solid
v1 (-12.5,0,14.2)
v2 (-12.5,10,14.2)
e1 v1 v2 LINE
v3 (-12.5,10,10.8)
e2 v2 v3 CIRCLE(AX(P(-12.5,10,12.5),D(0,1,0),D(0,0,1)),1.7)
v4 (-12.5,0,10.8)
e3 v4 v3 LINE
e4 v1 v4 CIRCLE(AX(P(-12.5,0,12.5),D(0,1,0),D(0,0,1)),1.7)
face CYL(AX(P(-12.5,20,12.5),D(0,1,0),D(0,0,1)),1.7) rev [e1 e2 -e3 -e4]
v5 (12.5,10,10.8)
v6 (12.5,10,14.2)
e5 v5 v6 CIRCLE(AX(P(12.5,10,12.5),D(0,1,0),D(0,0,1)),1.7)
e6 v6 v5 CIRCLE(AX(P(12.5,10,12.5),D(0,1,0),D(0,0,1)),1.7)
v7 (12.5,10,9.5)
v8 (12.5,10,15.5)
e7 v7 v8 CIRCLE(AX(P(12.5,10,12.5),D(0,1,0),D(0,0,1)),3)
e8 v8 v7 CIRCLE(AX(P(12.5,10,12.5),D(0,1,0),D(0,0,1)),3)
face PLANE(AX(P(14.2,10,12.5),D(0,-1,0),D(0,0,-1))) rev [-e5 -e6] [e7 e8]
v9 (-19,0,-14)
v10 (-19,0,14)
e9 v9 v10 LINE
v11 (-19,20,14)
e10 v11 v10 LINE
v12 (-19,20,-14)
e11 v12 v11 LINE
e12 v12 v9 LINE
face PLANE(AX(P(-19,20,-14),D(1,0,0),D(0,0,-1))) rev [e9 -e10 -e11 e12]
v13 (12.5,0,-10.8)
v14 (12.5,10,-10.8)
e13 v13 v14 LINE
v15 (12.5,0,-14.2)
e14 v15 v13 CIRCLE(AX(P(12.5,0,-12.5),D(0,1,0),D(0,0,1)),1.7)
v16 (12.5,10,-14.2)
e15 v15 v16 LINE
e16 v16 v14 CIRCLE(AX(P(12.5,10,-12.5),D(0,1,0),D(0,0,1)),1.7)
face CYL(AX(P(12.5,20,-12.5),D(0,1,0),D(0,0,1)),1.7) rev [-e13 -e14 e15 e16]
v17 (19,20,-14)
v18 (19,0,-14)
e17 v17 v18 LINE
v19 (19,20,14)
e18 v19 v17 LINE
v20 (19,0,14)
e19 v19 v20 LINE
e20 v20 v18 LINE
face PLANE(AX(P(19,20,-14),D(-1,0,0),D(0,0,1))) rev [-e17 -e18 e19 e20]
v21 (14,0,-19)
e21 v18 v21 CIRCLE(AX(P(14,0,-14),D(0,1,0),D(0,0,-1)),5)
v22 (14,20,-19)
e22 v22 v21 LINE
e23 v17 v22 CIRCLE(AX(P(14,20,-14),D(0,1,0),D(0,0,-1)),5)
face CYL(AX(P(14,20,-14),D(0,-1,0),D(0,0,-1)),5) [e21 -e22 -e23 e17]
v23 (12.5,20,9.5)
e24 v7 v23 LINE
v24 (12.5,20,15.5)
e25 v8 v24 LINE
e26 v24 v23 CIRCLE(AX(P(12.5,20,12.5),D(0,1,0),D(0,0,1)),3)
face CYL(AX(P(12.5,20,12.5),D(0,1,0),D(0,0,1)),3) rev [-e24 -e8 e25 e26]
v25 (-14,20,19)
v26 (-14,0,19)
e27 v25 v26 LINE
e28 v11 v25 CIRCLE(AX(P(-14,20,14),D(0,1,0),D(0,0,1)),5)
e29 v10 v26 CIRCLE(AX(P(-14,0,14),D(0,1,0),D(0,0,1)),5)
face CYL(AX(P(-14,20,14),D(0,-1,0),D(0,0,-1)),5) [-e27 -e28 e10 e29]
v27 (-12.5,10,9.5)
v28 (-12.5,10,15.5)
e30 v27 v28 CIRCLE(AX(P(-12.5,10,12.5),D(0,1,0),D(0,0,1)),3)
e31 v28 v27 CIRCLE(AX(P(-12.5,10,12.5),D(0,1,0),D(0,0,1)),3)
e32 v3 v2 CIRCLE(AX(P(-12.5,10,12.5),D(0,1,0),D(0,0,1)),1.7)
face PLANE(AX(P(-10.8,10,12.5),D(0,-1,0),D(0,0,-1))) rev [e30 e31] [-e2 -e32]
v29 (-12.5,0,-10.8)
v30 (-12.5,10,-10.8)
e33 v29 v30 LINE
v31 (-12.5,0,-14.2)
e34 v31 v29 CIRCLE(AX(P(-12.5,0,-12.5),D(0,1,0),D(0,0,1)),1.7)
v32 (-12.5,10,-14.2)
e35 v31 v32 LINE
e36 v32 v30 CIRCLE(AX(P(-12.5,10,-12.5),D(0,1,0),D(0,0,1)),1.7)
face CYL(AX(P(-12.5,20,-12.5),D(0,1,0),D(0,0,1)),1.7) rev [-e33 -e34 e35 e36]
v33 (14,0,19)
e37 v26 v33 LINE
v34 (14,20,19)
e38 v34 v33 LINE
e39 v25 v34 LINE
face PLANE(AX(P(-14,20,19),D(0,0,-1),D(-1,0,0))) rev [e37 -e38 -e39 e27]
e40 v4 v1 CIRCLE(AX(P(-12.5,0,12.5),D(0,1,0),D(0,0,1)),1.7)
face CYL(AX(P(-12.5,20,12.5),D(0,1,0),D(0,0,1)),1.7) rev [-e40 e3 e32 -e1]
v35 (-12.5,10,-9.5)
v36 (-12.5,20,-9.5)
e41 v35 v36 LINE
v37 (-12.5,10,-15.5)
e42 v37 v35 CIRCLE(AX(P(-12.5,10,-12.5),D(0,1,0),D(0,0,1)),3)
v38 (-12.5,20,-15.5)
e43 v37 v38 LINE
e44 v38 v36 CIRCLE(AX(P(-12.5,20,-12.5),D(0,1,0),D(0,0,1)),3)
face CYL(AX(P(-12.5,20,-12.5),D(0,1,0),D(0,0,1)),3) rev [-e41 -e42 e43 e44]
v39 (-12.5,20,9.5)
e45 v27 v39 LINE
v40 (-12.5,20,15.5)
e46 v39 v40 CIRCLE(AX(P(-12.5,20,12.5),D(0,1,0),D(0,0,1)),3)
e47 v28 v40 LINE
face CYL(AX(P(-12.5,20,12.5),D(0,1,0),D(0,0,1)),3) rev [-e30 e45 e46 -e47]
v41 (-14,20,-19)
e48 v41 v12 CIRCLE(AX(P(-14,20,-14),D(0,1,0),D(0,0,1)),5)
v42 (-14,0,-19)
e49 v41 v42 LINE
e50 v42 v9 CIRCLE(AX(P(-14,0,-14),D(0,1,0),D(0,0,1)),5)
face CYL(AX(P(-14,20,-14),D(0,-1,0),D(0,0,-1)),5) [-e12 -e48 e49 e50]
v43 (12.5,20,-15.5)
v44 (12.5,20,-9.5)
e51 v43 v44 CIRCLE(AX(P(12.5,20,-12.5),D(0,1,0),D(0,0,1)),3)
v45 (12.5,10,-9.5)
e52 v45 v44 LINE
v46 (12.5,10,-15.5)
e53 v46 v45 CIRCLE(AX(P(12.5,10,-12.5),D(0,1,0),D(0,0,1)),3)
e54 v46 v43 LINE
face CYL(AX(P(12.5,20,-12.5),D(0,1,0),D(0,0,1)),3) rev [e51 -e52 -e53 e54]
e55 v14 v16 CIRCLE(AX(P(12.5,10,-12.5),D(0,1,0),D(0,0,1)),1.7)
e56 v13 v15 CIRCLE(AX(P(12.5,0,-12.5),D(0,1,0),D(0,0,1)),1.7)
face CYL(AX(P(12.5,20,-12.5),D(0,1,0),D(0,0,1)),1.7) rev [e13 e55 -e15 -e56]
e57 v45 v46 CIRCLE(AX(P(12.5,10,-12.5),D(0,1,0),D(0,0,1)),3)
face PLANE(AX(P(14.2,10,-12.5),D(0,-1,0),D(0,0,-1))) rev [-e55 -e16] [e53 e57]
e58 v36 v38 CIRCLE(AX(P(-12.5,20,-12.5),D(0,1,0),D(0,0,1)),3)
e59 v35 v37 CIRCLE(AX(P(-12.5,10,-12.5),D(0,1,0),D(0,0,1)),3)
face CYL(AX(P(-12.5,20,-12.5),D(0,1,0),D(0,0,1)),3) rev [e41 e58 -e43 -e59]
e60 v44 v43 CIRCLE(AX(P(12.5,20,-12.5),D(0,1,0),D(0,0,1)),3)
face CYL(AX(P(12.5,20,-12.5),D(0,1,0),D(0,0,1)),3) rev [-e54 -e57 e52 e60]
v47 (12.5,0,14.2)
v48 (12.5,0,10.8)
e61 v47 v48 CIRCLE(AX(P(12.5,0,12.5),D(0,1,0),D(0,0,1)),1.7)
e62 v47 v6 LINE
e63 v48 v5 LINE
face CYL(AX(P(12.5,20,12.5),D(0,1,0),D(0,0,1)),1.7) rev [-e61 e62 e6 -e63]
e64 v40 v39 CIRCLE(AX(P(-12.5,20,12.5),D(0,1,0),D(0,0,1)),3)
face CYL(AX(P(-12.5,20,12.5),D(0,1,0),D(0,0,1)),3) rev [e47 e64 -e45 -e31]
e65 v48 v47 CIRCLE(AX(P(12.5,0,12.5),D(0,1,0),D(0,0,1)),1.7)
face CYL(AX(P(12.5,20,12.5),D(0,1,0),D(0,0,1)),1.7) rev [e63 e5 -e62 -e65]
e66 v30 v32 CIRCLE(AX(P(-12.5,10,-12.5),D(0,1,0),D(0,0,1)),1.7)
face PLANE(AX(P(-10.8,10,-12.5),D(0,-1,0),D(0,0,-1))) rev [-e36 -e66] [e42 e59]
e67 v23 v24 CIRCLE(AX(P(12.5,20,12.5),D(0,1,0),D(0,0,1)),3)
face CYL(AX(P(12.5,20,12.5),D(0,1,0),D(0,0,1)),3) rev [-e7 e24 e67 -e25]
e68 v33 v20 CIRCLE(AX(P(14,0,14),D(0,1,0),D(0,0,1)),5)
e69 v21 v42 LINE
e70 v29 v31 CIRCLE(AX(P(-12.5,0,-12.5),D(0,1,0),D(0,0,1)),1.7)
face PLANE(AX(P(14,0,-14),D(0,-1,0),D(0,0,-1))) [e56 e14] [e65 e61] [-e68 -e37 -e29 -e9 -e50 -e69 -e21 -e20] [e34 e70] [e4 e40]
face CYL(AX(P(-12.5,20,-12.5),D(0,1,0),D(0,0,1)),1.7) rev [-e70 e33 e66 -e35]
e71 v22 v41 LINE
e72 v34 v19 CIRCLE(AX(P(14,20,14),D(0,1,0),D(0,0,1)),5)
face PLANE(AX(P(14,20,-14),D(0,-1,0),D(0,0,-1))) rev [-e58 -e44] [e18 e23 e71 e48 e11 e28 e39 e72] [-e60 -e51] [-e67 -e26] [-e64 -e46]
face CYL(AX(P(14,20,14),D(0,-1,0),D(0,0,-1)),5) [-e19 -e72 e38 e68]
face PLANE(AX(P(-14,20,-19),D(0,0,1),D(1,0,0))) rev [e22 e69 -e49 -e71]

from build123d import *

# Parameters (mm, degrees)
BOSS_EXTRUDE1_DEPTH                                = 20
HOLE_SIZE_BASED_ON_SOCKET_HEAD_CAP_SCR_D           = 3.4
HOLE_SIZE_BASED_ON_SOCKET_HEAD_CAP_SCR_CBORE_D     = 6
HOLE_SIZE_BASED_ON_SOCKET_HEAD_CAP_SCR_CBORE_DEPTH = 10


with BuildPart() as part:
    # Sketch1 → Boss-Extrude1 (new body)
    with BuildSketch(Plane(origin=(0, 0, 0), x_dir=(1, 0, 0), z_dir=(0, 1, 0))):
        with BuildLine():
            Line((-14, 19), (14, 19))
            ThreePointArc((14, 19), (17.535533906, 17.535533906), (19, 14))
            Line((19, 14), (19, -14))
            ThreePointArc((19, -14), (17.535533906, -17.535533906), (14, -19))
            Line((14, -19), (-14, -19))
            ThreePointArc((-14, -19), (-17.535533906, -17.535533906), (-19, -14))
            Line((-19, -14), (-19, 14))
            ThreePointArc((-19, 14), (-17.535533906, 17.535533906), (-14, 19))
        make_face()
    extrude(amount=BOSS_EXTRUDE1_DEPTH)

    # Hole size (%based on) socket head cap screw type 1 (through all)
    with Locations(Plane(origin=(0, 20, 0), x_dir=(1, 0, 0), z_dir=(0, 1, 0))):
        with Locations((-12.5, 12.5), (12.5, 12.5), (12.5, -12.5), (-12.5, -12.5)):
            CounterBoreHole(HOLE_SIZE_BASED_ON_SOCKET_HEAD_CAP_SCR_D / 2, HOLE_SIZE_BASED_ON_SOCKET_HEAD_CAP_SCR_CBORE_D / 2, HOLE_SIZE_BASED_ON_SOCKET_HEAD_CAP_SCR_CBORE_DEPTH)


solid = part.part
